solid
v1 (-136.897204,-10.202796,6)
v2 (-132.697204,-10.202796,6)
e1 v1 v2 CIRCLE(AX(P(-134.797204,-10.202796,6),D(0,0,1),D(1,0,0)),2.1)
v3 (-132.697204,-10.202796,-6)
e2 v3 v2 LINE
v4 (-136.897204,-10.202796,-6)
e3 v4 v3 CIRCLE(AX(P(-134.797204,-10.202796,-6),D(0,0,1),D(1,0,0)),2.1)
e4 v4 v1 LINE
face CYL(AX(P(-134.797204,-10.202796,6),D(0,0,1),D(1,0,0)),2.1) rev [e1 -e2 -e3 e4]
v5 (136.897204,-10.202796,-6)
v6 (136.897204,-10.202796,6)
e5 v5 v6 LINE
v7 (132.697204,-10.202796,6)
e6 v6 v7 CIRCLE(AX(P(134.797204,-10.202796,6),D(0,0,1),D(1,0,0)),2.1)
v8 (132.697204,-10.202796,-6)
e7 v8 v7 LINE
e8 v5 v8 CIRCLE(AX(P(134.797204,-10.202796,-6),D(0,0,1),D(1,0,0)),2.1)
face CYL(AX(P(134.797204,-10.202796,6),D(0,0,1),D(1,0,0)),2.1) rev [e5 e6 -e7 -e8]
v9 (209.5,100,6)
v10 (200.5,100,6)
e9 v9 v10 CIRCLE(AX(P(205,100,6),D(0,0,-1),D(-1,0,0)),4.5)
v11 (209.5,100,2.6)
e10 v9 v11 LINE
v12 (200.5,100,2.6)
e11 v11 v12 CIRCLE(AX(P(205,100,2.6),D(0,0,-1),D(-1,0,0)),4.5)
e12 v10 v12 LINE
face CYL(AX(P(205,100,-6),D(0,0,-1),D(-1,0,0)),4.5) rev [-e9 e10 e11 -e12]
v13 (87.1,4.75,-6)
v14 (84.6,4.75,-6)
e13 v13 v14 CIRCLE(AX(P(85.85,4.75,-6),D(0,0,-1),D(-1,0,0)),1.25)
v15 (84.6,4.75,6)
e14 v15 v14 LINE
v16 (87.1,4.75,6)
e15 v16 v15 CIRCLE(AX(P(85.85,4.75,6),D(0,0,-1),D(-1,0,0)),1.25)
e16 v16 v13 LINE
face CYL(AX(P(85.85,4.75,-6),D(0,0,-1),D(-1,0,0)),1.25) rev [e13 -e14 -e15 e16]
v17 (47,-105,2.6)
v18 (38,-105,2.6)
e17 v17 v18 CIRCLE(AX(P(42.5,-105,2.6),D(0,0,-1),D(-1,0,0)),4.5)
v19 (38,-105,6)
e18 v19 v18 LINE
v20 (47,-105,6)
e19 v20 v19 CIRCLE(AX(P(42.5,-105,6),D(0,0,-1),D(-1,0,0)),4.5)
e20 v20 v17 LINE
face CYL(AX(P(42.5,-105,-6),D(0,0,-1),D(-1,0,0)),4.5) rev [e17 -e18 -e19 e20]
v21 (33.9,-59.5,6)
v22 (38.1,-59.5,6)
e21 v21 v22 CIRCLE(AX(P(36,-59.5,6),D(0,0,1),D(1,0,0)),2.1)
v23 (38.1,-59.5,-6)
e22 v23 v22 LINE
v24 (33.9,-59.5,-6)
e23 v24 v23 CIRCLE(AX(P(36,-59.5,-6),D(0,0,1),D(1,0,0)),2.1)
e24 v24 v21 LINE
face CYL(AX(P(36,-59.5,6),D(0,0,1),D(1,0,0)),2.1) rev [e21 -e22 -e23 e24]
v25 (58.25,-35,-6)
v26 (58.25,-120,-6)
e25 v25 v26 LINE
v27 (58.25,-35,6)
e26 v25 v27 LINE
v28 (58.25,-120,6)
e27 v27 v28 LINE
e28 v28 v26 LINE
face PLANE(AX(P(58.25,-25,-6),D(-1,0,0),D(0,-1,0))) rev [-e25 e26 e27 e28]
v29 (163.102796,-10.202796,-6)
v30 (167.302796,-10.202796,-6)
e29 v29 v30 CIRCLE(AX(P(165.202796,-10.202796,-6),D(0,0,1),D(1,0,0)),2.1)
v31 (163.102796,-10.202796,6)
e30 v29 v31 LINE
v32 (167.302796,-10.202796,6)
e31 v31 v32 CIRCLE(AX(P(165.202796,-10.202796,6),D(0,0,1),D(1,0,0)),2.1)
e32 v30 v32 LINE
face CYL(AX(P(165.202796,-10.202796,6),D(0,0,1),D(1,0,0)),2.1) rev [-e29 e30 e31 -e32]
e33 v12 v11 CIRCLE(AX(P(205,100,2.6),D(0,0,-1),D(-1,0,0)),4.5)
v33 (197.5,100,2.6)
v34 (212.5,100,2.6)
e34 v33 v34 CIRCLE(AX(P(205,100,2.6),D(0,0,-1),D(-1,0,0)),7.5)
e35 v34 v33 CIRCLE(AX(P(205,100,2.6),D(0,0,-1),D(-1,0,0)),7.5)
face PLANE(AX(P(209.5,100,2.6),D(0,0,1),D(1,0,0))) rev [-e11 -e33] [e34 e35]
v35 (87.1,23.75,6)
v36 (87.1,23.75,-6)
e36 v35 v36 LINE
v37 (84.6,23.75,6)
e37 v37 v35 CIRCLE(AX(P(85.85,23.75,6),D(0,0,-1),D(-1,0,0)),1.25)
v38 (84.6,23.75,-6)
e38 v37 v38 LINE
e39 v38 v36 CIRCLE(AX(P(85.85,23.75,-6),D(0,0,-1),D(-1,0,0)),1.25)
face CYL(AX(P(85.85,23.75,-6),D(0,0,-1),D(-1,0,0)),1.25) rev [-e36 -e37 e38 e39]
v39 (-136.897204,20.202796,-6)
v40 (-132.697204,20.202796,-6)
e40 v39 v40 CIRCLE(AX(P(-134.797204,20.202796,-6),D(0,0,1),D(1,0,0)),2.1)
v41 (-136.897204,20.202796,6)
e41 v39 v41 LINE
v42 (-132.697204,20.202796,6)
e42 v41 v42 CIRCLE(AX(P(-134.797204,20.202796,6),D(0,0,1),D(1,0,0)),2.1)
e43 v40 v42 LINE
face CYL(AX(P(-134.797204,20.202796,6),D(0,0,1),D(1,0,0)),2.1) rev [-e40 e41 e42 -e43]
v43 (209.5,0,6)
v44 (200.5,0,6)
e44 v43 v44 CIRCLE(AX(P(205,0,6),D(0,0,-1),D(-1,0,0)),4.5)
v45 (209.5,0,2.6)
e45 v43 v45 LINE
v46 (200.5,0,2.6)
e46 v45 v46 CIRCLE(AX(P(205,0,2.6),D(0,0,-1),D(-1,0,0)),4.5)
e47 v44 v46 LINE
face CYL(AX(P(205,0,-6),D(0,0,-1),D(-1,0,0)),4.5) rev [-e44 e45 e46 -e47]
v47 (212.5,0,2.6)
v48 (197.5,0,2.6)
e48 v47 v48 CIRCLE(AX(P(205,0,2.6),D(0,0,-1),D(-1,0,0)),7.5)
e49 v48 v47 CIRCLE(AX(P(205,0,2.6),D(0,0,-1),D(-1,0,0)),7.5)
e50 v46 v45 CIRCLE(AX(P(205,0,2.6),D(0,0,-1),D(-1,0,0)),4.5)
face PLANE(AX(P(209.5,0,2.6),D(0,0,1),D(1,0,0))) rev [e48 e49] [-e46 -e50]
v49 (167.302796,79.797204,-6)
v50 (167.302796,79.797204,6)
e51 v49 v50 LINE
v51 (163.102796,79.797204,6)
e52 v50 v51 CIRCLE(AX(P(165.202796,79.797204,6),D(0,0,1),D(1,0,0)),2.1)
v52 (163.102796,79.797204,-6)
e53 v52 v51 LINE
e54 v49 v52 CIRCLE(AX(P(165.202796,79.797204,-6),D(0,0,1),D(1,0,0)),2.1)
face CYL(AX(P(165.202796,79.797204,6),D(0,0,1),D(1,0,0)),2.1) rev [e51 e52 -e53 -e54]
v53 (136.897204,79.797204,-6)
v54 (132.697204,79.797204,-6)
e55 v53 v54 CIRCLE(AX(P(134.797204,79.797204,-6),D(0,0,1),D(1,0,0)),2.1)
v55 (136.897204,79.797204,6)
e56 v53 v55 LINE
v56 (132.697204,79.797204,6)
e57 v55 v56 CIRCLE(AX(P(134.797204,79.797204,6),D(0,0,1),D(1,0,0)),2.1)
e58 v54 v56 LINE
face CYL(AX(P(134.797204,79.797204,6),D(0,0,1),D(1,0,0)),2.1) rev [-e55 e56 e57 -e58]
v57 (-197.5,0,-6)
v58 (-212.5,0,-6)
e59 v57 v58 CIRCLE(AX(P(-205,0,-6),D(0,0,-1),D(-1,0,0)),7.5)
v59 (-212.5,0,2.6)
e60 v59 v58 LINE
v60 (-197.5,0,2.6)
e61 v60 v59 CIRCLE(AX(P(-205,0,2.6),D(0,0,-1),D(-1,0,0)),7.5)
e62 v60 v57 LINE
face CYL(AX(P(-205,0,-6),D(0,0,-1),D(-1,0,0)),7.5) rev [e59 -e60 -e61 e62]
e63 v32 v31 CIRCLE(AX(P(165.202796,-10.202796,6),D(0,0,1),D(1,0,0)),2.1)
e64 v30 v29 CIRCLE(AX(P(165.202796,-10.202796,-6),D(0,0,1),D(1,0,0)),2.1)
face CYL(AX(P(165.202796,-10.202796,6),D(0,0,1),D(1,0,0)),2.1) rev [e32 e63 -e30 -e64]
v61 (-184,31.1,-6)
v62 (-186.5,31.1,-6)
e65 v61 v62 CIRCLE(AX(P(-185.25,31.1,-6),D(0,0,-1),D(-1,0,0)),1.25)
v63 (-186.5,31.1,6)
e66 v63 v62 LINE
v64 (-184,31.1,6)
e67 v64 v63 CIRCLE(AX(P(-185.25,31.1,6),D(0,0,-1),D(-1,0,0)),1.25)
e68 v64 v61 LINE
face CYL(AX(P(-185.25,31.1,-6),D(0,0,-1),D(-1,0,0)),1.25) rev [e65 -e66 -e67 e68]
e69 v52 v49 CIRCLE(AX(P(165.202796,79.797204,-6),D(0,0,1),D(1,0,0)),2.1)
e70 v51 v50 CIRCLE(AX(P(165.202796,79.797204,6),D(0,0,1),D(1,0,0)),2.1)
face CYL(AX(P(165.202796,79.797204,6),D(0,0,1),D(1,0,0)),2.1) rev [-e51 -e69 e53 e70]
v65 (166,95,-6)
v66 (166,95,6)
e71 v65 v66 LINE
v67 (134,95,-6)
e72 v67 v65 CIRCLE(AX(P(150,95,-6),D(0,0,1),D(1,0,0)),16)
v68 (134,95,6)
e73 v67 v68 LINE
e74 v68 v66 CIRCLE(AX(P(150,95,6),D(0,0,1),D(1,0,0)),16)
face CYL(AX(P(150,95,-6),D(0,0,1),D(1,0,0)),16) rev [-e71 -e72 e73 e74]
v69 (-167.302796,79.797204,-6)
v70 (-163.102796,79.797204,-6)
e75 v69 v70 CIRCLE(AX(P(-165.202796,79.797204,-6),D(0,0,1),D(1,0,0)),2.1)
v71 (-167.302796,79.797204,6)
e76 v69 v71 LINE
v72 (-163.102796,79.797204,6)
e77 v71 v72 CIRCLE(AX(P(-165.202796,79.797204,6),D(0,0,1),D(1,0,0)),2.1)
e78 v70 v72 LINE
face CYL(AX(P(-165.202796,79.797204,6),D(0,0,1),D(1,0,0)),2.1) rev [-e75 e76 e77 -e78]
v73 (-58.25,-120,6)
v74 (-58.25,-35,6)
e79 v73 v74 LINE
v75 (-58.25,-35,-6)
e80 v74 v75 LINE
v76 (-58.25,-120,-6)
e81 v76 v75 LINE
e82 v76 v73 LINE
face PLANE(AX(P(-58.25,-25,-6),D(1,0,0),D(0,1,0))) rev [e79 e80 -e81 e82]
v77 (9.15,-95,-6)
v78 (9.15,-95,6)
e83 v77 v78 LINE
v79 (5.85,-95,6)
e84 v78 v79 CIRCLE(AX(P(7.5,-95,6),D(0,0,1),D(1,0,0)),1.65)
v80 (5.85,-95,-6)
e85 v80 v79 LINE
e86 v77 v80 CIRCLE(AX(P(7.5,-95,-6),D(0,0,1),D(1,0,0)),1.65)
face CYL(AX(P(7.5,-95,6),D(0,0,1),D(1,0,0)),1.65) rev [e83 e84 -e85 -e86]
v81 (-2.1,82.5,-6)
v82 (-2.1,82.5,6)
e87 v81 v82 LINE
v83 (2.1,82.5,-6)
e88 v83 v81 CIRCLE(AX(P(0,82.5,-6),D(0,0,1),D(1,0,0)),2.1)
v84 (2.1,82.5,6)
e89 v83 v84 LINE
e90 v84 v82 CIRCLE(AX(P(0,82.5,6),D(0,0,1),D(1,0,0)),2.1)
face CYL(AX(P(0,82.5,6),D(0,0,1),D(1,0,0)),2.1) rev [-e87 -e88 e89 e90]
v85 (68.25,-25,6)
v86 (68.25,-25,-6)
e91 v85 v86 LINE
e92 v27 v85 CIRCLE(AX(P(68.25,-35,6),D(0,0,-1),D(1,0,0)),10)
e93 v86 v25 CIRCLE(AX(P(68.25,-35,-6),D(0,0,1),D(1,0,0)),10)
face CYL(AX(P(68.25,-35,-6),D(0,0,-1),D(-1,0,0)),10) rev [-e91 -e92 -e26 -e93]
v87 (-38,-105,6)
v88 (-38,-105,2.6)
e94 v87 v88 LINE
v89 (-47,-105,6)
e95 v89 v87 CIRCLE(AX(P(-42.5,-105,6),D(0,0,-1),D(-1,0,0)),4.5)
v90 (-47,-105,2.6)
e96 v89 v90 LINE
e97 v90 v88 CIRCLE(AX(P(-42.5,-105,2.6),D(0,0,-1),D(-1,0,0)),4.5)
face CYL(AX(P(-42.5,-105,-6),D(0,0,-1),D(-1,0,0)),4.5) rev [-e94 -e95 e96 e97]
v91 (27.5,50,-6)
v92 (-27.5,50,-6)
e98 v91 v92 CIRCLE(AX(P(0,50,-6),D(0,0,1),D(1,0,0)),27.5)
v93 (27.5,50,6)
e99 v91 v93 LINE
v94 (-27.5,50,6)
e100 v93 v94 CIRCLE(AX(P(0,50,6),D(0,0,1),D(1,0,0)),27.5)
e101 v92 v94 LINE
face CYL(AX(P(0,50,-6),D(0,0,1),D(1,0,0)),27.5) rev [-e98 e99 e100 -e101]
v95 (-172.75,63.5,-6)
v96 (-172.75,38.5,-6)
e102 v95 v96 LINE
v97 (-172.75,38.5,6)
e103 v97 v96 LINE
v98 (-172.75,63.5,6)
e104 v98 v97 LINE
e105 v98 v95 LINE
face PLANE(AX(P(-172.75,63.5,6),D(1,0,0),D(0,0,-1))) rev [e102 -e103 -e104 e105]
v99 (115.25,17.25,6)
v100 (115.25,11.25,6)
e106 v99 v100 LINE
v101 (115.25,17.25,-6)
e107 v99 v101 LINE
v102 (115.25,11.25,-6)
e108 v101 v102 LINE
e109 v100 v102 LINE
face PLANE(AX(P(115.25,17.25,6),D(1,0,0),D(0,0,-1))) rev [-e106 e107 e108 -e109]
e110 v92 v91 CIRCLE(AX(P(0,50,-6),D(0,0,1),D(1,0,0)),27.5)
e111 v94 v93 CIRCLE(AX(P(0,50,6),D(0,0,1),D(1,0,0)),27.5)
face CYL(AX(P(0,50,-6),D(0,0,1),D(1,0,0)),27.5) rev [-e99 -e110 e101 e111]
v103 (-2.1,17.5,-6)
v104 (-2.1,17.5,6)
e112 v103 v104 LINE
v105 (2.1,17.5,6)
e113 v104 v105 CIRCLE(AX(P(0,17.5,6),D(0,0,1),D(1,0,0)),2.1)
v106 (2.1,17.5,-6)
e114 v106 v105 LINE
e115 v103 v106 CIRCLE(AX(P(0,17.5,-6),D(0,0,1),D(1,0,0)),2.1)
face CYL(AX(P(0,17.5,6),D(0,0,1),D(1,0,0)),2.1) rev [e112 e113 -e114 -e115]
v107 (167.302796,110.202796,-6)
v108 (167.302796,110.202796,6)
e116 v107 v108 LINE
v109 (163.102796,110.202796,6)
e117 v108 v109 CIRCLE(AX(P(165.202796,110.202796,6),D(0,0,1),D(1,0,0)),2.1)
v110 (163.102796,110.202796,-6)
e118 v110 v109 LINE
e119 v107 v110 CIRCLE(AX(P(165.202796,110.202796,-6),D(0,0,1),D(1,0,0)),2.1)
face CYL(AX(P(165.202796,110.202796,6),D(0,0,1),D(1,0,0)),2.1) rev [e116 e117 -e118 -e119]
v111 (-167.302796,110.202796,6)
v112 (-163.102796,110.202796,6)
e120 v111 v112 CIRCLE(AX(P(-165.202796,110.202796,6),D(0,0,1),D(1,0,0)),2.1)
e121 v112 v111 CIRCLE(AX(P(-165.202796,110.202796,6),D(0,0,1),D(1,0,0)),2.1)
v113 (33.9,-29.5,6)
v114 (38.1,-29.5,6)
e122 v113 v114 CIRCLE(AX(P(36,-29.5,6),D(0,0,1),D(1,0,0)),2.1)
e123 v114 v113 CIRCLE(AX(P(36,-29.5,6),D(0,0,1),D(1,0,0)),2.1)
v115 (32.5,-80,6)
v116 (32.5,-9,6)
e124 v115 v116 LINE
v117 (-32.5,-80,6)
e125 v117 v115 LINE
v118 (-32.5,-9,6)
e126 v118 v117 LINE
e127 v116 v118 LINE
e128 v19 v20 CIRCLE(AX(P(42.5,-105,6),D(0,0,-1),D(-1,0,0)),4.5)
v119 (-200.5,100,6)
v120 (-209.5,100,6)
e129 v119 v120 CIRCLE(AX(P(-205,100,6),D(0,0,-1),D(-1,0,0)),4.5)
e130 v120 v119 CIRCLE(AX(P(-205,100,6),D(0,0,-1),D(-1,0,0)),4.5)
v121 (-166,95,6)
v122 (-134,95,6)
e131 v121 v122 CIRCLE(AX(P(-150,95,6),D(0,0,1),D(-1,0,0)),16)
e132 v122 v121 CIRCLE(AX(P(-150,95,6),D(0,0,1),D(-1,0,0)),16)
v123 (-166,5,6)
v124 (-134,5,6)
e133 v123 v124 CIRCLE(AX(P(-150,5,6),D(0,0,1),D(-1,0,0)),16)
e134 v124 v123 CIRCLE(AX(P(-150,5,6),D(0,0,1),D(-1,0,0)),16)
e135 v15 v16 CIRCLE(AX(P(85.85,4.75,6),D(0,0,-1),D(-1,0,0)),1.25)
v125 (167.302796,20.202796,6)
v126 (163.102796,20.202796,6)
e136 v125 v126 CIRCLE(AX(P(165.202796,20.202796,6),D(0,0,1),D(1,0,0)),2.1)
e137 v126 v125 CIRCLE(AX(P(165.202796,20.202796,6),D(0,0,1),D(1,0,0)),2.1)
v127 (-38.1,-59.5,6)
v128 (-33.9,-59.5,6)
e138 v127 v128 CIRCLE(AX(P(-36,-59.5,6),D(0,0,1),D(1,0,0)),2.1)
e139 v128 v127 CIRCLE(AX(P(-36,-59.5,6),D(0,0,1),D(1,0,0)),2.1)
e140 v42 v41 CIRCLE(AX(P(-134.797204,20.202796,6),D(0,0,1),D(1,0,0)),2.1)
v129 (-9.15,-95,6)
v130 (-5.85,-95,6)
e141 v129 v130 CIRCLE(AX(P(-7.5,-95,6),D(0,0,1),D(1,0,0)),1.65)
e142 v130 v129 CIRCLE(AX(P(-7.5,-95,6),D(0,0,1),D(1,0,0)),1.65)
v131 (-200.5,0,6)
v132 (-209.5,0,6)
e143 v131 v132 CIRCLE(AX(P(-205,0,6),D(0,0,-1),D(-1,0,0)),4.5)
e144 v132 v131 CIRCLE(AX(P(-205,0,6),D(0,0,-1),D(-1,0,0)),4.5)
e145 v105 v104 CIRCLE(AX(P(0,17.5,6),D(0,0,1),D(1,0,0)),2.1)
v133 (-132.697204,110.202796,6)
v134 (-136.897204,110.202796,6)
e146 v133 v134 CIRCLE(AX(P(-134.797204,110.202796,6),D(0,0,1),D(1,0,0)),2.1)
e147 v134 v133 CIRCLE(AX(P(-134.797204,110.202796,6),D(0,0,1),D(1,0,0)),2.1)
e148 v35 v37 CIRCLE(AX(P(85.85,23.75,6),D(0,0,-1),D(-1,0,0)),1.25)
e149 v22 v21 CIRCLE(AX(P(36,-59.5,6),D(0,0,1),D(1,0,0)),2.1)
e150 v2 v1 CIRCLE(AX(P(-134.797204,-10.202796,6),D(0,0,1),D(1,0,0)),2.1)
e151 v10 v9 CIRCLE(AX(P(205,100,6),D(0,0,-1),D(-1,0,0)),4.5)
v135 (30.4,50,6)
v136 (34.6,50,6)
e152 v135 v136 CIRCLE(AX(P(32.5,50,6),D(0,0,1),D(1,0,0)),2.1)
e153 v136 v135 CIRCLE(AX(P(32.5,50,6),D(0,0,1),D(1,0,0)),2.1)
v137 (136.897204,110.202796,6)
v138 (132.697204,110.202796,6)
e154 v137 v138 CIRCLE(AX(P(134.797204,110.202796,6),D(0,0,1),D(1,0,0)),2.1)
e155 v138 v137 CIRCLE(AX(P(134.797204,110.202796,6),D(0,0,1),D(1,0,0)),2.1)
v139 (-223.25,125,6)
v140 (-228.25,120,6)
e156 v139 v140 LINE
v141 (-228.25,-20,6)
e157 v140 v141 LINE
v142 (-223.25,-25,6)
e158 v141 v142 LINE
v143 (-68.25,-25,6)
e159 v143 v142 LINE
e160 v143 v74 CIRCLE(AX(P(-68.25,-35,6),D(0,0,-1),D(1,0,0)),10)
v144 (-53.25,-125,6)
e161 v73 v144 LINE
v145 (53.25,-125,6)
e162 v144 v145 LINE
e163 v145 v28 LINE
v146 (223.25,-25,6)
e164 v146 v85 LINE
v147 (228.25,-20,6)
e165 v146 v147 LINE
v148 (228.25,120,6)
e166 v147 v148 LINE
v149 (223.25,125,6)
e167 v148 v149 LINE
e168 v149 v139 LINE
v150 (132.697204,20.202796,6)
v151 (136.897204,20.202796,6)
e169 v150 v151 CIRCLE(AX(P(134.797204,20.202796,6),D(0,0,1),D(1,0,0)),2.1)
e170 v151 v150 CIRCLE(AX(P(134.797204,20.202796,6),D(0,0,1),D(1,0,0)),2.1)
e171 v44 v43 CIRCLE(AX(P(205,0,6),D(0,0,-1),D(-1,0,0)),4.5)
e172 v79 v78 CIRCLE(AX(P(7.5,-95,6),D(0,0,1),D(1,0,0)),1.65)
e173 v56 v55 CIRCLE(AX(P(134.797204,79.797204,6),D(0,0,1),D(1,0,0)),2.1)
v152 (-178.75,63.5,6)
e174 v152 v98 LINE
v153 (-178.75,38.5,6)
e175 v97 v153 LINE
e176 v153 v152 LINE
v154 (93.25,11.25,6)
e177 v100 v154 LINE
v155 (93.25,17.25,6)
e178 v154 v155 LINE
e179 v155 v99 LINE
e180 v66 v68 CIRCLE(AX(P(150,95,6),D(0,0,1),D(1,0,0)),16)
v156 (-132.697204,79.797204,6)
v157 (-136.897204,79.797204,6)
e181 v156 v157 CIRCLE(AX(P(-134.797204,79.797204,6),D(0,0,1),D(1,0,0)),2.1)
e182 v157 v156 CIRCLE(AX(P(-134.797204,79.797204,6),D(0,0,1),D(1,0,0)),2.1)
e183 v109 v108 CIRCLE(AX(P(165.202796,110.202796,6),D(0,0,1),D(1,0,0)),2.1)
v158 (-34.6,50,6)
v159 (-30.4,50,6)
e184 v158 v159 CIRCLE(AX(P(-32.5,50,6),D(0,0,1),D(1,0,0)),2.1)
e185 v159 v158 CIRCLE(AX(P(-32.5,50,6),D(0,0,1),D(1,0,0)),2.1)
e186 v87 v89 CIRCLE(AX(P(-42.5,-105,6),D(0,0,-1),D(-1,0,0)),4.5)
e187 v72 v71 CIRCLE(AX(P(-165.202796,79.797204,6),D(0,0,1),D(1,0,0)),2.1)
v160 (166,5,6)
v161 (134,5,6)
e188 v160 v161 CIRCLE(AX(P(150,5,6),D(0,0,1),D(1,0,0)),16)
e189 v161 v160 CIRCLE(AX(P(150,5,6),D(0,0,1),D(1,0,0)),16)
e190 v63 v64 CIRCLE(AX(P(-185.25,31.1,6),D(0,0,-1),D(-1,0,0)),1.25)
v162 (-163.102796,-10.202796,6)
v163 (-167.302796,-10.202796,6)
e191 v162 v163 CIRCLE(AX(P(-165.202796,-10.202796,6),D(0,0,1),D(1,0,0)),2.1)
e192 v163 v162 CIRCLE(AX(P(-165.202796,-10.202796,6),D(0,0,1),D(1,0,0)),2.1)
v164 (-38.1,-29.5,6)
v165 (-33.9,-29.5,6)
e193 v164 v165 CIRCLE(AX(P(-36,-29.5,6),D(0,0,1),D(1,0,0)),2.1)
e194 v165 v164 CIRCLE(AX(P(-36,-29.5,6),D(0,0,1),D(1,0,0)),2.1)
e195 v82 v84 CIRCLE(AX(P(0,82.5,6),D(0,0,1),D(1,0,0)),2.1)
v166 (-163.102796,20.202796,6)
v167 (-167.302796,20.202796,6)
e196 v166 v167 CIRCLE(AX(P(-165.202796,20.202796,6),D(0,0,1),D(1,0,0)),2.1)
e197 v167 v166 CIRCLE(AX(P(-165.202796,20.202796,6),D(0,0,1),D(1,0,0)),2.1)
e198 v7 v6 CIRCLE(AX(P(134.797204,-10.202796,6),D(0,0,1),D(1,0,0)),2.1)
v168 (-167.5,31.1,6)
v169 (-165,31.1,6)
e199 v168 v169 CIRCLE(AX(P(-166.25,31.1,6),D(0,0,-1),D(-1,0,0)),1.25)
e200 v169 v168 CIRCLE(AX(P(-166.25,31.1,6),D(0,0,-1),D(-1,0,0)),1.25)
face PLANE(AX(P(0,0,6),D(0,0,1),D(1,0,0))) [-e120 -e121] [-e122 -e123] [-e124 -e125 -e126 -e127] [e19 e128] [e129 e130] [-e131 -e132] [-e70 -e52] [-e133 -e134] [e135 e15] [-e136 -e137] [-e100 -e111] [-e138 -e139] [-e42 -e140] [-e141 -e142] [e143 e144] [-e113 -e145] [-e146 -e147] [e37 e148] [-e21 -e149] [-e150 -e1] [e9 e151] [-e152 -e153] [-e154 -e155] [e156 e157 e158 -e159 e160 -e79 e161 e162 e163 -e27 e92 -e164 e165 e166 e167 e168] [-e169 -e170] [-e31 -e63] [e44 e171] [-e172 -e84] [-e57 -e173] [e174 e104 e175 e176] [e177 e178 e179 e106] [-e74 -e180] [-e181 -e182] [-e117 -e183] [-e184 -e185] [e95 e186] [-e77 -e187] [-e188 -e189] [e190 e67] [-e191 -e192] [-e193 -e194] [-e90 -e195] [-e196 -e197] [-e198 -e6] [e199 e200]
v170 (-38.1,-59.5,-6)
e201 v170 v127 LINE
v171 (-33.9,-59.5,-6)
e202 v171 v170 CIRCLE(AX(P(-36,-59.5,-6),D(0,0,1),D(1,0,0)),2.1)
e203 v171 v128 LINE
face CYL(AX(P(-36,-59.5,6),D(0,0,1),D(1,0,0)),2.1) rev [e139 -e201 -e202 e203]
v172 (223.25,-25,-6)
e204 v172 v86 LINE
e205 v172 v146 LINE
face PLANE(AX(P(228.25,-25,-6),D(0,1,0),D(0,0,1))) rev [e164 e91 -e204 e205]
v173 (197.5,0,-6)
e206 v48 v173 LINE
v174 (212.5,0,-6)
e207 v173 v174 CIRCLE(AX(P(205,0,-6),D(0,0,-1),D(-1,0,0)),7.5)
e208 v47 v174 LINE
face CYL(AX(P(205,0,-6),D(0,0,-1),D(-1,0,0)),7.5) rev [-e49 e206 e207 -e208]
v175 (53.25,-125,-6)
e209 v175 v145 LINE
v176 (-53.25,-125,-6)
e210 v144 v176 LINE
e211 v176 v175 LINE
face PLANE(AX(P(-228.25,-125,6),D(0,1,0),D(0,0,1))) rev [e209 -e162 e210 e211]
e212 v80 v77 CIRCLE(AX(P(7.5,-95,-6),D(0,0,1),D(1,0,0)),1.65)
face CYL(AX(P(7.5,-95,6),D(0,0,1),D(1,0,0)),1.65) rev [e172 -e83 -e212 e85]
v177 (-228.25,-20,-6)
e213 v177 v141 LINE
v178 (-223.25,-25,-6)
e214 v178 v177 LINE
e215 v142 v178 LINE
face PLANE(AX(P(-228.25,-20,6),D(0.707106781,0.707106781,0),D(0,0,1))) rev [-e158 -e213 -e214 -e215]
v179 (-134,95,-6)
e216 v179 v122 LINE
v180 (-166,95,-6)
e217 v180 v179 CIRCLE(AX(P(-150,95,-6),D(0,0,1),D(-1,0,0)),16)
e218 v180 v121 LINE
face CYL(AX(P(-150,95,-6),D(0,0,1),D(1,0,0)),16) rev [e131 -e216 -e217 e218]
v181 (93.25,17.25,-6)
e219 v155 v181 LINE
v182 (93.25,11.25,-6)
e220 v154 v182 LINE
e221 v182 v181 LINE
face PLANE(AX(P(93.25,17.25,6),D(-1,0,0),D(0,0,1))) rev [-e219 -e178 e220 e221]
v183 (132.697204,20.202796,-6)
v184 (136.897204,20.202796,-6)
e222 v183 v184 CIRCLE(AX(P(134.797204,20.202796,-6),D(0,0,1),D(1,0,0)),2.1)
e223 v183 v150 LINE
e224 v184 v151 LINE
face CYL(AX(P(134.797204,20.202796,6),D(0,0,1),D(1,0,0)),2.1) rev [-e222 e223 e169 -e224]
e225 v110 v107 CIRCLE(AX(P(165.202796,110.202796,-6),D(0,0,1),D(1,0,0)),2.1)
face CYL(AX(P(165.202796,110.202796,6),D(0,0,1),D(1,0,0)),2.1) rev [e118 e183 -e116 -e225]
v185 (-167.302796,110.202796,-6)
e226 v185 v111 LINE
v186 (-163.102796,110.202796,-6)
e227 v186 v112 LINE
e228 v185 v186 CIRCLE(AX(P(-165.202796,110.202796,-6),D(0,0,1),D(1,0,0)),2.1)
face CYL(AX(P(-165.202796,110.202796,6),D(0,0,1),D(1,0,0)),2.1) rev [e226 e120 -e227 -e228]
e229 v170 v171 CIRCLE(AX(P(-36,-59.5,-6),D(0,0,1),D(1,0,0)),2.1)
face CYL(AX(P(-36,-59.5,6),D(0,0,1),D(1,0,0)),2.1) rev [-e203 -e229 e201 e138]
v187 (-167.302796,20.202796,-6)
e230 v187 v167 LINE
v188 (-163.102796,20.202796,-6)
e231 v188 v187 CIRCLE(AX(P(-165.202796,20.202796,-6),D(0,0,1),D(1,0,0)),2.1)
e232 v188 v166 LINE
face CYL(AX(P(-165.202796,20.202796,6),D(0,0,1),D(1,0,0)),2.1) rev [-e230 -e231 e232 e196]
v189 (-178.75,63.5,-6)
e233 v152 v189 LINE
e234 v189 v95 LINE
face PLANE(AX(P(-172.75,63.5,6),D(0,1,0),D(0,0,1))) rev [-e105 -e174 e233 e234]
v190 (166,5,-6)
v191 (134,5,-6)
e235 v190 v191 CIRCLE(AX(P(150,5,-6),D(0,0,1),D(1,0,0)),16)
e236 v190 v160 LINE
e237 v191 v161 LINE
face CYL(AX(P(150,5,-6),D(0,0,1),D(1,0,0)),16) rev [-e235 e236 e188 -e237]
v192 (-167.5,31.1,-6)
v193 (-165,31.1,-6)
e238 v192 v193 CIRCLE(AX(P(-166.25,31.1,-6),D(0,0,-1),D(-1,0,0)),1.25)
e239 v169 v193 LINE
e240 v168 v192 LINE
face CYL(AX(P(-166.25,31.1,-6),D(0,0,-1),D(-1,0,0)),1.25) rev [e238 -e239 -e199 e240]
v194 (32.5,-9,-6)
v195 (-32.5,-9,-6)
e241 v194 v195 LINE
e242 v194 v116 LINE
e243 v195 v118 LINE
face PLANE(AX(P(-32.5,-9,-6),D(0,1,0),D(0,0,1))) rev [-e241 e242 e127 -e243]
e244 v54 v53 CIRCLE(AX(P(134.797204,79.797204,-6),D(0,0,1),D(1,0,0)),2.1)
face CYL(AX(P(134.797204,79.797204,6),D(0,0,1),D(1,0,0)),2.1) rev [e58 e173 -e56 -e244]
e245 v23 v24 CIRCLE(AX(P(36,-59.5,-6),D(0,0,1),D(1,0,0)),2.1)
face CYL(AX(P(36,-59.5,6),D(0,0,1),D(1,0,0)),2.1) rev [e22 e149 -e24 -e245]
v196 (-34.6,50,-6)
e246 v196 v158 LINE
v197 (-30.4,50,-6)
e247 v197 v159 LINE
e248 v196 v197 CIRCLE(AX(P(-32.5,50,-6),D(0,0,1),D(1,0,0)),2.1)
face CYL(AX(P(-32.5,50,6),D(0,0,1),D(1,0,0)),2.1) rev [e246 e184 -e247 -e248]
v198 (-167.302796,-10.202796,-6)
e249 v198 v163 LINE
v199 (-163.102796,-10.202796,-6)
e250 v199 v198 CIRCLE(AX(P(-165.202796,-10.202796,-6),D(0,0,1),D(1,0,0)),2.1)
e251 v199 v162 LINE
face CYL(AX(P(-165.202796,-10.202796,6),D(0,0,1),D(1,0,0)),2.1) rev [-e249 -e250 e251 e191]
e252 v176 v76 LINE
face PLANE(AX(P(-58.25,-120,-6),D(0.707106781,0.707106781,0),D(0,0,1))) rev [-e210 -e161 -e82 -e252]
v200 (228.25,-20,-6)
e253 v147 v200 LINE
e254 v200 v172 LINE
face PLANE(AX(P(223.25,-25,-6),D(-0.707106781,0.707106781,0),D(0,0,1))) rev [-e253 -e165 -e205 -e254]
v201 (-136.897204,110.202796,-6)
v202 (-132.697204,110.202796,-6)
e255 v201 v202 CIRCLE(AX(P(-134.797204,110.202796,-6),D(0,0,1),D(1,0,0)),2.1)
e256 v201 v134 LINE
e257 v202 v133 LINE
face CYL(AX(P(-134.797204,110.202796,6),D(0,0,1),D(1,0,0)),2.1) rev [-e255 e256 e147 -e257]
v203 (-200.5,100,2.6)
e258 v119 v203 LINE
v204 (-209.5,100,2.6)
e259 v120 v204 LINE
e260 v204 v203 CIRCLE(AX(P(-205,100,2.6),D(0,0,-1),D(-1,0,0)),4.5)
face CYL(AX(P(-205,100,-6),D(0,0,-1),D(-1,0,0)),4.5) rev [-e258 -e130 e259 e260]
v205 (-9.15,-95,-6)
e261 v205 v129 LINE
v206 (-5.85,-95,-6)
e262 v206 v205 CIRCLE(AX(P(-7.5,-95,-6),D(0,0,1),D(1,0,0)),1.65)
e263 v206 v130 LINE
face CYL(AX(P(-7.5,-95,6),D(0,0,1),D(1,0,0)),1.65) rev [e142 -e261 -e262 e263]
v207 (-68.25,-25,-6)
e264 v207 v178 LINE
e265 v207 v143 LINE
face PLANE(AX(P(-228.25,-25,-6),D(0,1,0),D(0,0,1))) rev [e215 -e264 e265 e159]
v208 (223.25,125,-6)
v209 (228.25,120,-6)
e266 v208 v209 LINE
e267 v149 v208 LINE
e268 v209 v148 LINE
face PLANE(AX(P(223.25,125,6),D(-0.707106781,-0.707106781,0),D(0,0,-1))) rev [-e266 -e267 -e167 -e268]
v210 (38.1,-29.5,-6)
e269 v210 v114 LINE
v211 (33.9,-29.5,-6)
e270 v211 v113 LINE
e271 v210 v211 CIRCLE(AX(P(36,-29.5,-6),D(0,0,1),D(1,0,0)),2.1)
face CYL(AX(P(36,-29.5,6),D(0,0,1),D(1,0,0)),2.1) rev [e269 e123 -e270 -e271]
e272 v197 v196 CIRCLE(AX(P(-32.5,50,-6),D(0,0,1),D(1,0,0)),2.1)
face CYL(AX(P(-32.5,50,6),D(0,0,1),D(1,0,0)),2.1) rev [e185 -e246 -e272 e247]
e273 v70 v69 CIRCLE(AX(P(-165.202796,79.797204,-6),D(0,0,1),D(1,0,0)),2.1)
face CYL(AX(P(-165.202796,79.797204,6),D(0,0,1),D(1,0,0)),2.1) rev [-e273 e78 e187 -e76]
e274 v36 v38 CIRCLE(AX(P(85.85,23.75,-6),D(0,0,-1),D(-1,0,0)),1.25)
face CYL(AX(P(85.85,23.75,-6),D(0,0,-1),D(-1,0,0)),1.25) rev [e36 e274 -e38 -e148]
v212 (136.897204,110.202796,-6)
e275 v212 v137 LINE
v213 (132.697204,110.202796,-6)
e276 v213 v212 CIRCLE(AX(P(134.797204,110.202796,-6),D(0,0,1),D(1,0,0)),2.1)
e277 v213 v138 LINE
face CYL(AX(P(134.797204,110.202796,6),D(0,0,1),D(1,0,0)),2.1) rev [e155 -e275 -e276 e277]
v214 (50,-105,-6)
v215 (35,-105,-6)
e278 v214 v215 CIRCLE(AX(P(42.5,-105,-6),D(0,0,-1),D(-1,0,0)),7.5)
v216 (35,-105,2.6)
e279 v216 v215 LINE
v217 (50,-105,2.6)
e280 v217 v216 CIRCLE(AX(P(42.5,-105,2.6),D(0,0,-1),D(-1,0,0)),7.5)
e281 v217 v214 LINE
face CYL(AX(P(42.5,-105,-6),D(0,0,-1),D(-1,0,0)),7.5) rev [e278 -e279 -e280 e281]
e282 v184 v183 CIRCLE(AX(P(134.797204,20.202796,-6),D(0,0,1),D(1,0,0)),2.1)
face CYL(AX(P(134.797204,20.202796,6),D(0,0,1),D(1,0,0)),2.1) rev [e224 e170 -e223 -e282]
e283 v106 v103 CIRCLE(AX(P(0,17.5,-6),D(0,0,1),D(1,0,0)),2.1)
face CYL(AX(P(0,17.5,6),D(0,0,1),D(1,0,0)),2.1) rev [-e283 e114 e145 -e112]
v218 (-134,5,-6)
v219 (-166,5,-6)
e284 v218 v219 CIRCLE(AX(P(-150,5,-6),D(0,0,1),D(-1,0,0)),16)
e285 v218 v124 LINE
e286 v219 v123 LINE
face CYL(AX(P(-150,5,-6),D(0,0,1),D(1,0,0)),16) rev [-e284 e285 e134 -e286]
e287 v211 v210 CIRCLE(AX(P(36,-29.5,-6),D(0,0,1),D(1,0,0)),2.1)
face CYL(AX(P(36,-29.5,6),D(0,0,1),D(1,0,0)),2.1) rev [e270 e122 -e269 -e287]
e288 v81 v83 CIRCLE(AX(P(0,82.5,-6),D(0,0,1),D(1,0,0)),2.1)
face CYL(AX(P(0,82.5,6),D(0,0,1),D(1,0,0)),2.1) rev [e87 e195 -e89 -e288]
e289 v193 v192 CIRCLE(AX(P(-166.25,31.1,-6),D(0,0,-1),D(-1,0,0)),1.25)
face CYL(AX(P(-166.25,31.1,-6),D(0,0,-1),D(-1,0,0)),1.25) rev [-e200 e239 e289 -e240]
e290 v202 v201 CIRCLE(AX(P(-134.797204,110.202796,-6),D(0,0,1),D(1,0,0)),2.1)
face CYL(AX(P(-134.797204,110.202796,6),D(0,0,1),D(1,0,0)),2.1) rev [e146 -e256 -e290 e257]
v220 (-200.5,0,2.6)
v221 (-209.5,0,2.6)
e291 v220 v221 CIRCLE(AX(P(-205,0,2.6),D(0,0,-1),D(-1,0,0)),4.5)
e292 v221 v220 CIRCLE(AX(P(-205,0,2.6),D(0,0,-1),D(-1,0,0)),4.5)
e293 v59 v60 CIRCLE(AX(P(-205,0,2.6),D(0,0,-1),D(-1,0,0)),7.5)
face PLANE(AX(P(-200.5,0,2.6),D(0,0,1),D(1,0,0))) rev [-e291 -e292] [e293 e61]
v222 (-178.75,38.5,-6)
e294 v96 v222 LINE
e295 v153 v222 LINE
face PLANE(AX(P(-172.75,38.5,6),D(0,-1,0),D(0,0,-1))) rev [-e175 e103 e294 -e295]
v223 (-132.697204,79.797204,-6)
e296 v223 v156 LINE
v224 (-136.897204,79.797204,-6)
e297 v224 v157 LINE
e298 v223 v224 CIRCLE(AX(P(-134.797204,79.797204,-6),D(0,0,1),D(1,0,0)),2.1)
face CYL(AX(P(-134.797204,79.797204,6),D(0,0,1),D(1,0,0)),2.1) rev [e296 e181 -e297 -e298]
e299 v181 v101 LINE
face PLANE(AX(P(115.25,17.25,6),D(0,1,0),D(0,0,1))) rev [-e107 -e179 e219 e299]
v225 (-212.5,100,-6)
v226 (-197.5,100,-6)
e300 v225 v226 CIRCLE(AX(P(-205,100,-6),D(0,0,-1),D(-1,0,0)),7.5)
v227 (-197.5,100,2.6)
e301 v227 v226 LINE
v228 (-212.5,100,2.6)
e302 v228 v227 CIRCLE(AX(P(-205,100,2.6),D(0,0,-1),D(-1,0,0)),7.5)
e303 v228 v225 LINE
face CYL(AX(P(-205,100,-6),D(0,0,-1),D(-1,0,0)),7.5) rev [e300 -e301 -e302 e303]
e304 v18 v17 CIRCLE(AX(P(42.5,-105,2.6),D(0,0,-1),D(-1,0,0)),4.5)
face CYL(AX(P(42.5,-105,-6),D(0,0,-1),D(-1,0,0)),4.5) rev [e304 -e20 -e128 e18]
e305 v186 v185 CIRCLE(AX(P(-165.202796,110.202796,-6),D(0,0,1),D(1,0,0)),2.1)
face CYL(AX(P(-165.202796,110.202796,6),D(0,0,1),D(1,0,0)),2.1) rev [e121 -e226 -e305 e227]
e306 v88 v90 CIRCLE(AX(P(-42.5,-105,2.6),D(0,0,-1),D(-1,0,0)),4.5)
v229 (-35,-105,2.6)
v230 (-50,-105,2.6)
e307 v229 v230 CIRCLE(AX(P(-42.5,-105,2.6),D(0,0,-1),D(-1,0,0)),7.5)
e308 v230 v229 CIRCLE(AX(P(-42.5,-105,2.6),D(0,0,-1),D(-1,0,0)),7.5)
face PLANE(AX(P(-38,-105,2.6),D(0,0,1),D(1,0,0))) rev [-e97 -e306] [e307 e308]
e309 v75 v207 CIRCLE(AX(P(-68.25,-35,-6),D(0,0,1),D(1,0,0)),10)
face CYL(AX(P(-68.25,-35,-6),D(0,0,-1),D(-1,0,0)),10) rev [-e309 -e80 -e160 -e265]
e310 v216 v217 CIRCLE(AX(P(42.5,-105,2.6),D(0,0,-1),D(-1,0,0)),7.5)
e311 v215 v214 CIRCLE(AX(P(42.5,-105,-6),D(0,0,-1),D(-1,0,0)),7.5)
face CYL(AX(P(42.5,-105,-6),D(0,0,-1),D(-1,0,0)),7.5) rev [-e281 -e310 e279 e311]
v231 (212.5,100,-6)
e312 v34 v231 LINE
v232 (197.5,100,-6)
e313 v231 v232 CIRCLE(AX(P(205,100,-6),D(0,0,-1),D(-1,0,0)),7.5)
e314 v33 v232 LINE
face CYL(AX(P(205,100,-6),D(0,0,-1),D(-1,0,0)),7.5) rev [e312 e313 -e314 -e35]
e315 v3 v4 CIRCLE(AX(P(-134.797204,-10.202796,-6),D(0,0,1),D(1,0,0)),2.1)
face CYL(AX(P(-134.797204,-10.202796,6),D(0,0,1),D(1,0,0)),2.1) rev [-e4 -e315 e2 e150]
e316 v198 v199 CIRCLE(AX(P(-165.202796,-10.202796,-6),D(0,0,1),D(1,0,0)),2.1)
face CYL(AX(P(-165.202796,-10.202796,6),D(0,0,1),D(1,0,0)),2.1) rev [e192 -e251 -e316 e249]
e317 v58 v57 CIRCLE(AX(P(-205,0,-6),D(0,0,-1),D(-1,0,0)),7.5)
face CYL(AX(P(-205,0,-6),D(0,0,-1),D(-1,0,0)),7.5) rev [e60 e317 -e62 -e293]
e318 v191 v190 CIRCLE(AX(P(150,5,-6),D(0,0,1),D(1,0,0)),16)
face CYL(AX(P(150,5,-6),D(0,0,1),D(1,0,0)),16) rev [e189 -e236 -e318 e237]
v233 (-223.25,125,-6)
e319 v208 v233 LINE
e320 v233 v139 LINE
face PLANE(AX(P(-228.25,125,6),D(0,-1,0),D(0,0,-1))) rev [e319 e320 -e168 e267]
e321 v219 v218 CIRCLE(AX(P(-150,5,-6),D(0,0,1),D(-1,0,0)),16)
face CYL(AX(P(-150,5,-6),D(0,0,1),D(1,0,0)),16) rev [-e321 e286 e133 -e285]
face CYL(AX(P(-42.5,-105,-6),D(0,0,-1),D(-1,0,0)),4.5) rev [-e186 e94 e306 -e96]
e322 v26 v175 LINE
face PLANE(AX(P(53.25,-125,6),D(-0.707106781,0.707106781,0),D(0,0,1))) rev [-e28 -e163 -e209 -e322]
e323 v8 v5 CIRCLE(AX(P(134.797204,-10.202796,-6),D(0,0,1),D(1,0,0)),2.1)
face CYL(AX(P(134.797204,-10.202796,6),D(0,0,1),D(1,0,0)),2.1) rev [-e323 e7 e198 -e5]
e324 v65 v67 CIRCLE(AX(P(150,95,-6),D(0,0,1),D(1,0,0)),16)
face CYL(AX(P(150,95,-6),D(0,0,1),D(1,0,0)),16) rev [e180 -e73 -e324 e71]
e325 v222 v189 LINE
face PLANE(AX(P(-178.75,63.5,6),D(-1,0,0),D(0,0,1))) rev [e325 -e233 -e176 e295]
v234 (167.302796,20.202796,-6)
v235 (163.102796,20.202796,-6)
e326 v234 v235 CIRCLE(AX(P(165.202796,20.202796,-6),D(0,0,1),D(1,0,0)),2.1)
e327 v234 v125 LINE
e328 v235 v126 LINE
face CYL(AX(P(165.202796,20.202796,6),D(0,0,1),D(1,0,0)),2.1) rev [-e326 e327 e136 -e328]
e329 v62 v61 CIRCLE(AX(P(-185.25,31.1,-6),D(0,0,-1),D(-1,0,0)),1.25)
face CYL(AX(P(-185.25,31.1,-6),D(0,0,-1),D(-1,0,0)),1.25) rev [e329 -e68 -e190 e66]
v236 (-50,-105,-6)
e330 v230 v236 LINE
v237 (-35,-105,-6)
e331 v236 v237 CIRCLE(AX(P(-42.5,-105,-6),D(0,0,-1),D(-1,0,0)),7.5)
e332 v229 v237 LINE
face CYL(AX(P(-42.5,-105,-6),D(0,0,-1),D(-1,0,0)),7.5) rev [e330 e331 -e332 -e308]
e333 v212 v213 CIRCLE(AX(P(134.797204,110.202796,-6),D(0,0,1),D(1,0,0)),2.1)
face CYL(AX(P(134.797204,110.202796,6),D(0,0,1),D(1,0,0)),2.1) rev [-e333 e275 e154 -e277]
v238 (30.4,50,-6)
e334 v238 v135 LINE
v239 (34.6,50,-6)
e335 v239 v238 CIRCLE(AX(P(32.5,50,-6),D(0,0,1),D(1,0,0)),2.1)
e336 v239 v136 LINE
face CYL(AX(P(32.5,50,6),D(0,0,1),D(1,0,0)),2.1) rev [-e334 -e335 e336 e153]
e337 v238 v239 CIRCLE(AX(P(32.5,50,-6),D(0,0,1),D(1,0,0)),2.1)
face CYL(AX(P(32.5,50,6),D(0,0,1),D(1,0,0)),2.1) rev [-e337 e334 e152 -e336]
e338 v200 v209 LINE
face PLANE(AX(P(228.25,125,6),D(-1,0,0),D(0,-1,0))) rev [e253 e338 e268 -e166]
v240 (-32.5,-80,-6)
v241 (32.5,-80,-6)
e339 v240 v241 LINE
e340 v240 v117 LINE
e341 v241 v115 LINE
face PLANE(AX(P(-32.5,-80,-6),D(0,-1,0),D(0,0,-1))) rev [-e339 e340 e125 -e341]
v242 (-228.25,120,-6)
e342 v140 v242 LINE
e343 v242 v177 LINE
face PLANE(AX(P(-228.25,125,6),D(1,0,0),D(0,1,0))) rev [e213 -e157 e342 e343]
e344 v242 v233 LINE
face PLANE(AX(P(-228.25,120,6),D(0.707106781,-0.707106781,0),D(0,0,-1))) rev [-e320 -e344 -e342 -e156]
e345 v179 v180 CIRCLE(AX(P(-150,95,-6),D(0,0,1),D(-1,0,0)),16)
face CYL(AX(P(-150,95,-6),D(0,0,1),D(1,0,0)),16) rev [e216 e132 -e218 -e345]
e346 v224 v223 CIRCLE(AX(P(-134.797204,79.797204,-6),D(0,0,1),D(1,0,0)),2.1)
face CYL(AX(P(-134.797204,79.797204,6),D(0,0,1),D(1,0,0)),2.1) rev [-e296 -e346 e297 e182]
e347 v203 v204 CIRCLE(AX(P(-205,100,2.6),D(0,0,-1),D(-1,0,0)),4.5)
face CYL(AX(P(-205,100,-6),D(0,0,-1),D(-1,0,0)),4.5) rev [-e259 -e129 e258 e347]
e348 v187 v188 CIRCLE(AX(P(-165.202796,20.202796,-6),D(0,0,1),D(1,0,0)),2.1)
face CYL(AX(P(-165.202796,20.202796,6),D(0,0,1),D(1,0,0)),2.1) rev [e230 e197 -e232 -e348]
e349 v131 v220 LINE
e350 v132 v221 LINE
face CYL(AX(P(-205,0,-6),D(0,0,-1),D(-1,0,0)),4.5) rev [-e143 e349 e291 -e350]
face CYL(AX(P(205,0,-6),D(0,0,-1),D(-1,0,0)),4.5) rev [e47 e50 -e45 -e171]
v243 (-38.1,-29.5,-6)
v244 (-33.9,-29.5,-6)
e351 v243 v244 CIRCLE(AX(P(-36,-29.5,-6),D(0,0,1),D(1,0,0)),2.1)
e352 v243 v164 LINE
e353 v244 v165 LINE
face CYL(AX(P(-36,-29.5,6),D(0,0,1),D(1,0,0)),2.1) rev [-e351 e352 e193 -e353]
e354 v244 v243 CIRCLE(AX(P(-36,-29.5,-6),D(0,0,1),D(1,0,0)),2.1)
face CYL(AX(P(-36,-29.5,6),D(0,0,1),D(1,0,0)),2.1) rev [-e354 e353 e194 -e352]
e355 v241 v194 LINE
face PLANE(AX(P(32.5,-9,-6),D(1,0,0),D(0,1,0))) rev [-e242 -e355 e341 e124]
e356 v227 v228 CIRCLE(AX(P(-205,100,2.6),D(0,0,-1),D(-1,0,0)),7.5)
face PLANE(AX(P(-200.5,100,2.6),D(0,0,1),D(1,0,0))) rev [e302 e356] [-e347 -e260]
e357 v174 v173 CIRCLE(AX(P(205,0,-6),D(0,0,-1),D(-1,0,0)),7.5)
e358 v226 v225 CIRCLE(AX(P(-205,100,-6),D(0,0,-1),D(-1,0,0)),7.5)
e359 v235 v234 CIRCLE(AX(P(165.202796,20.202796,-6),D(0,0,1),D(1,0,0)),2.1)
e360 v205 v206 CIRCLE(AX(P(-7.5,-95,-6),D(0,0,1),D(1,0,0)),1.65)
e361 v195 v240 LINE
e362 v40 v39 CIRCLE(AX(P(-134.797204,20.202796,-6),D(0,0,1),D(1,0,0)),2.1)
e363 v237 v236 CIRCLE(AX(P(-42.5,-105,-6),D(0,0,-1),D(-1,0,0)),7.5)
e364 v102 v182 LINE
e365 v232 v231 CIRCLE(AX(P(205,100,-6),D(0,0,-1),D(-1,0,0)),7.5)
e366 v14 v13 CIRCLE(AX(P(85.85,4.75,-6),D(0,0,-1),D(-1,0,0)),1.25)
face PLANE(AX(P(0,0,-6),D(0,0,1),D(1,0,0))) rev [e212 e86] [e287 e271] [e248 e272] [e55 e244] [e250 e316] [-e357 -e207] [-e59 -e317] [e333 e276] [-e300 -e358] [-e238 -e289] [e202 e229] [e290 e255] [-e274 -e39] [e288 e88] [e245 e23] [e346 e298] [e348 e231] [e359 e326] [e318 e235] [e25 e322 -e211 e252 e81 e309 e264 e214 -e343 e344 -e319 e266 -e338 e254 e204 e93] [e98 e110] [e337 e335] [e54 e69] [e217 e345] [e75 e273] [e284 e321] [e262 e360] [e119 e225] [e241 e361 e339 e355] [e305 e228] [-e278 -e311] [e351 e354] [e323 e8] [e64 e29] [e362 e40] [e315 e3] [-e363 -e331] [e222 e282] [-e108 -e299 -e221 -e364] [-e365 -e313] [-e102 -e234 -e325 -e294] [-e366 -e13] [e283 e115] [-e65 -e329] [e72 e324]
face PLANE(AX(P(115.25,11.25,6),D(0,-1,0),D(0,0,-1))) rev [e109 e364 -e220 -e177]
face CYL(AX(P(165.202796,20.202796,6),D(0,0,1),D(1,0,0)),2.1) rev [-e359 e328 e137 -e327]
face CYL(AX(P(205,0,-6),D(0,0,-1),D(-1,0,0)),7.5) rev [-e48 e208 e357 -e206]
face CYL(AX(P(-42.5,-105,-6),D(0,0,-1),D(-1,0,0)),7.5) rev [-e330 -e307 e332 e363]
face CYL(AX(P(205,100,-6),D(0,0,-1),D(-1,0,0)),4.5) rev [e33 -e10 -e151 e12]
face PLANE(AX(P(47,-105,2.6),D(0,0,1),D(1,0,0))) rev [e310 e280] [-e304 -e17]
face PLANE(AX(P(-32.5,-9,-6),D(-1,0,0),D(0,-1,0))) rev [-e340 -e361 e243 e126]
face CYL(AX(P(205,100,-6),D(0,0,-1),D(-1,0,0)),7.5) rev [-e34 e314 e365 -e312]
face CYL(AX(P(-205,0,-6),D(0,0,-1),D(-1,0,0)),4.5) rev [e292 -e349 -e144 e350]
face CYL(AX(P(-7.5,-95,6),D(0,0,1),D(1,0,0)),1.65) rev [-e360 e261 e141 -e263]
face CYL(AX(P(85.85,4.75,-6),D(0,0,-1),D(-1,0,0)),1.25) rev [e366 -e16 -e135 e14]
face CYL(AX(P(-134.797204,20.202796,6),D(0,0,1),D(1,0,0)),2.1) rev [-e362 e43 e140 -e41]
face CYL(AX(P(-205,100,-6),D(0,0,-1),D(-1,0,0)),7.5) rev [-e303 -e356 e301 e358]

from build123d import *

# Parameters (mm, degrees)
SKETCH1_W                                           = 456.5
SKETCH1_H                                           = 250
BOSS_EXTRUDE1_DEPTH                                 = 6
SKETCH2_W                                           = 170
SKETCH2_H                                           = 100
CUT_EXTRUDE1_DEPTH                                  = 12
SKETCH3_R                                           = 16
CUT_EXTRUDE2_DEPTH                                  = 261.513075488
M5_TAPPED_HOLE1_D                                   = 4.2
SKETCH6_R                                           = 27.5
CUT_EXTRUDE3_DEPTH                                  = 261.513075488
M5_TAPPED_HOLE2_D                                   = 4.2
SKETCH9_W                                           = 65
SKETCH9_H                                           = 71
CUT_EXTRUDE4_DEPTH                                  = 261.513075488
M5_TAPPED_HOLE3_D                                   = 4.2
M4_TAPPED_HOLE1_D                                   = 3.3
SKETCH14_W                                          = 22
SKETCH14_H                                          = 6
SKETCH14_W_2                                        = 6
SKETCH14_H_2                                        = 25
CUT_EXTRUDE5_DEPTH                                  = 261.513075488
M3_TAPPED_HOLE1_D                                   = 2.5
FILLET1_R                                           = 10
CHAMFER1_SIZE                                       = 5
CBORE_FOR_M8_HEX_SOCKET_HEAD_CAP_SCREW1_D           = 9
CBORE_FOR_M8_HEX_SOCKET_HEAD_CAP_SCREW1_CBORE_D     = 15
CBORE_FOR_M8_HEX_SOCKET_HEAD_CAP_SCREW1_CBORE_DEPTH = 8.6


with BuildPart() as part:
    # Sketch1 → Boss-Extrude1 (new, symmetric)
    with BuildSketch(Plane.XY):
        Rectangle(SKETCH1_W, SKETCH1_H)
    extrude(amount=BOSS_EXTRUDE1_DEPTH, both=True)

    # Sketch2 → Cut-Extrude1 (cut)
    with BuildSketch(Plane.XY.offset(6)):
        with Locations((-143.25, -75)):
            Rectangle(SKETCH2_W, SKETCH2_H)
        with Locations((143.25, -75)):
            Rectangle(SKETCH2_W, SKETCH2_H)
    extrude(amount=-CUT_EXTRUDE1_DEPTH, mode=Mode.SUBTRACT)

    # Sketch3 → Cut-Extrude2 (cut, through all)
    with BuildSketch(Plane.XY.offset(6)):
        with Locations((150, 95)):
            Circle(SKETCH3_R)
        with Locations((150, 5)):
            Circle(SKETCH3_R)
        with Locations(Location((-150, 5, 0), (0, 0, 180))):
            Circle(SKETCH3_R)
        with Locations(Location((-150, 95, 0), (0, 0, 180))):
            Circle(SKETCH3_R)
    extrude(amount=-CUT_EXTRUDE2_DEPTH, mode=Mode.SUBTRACT)

    # M5 Tapped Hole1 (through all)
    with Locations(Plane.XY.offset(6)):
        with Locations((134.797204204, 110.202795796), (165.202795796, 110.202795796), (134.797204204, 79.797204204), (165.202795796, 79.797204204), (134.797204204, 20.202795796), (165.202795796, 20.202795796), (134.797204204, -10.202795796), (165.202795796, -10.202795796), (-134.797204204, -10.202795796), (-165.202795796, -10.202795796), (-134.797204204, 20.202795796), (-165.202795796, 20.202795796), (-134.797204204, 79.797204204), (-165.202795796, 79.797204204), (-134.797204204, 110.202795796), (-165.202795796, 110.202795796)):
            Hole(M5_TAPPED_HOLE1_D / 2)

    # Sketch6 → Cut-Extrude3 (cut, through all)
    with BuildSketch(Plane.XY.offset(6)):
        with Locations((0, 50)):
            Circle(SKETCH6_R)
    extrude(amount=-CUT_EXTRUDE3_DEPTH, mode=Mode.SUBTRACT)

    # M5 Tapped Hole2 (through all)
    with Locations(Plane.XY.offset(6)):
        with Locations((32.5, 50), (0, 82.5), (-32.5, 50), (0, 17.5)):
            Hole(M5_TAPPED_HOLE2_D / 2)

    # Sketch9 → Cut-Extrude4 (cut, through all)
    with BuildSketch(Plane.XY.offset(6)):
        with Locations((0, -44.5)):
            Rectangle(SKETCH9_W, SKETCH9_H)
    extrude(amount=-CUT_EXTRUDE4_DEPTH, mode=Mode.SUBTRACT)

    # M5 Tapped Hole3 (through all)
    with Locations(Plane.XY.offset(6)):
        with Locations((36, -29.5), (36, -59.5), (-36, -59.5), (-36, -29.5)):
            Hole(M5_TAPPED_HOLE3_D / 2)

    # M4 Tapped Hole1 (through all)
    with Locations(Plane.XY.offset(6)):
        with Locations((-7.5, -95), (7.5, -95)):
            Hole(M4_TAPPED_HOLE1_D / 2)

    # Sketch14 → Cut-Extrude5 (cut, through all)
    with BuildSketch(Plane(origin=(0, 0, -6), x_dir=(-1, 0, 0), z_dir=(0, 0, -1))):
        with Locations((-104.25, 14.25)):
            Rectangle(SKETCH14_W, SKETCH14_H)
        with Locations((175.75, 51)):
            Rectangle(SKETCH14_W_2, SKETCH14_H_2)
    extrude(amount=-CUT_EXTRUDE5_DEPTH, mode=Mode.SUBTRACT)

    # M3 Tapped Hole1 (through all)
    with Locations(Plane(origin=(0, 0, -6), x_dir=(-1, 0, 0), z_dir=(0, 0, -1))):
        with Locations((-85.85, 23.75), (185.25, 31.1), (-85.85, 4.75), (166.25, 31.1)):
            Hole(M3_TAPPED_HOLE1_D / 2)

    # Fillet1
    fillet1_edges = [part.edges().sort_by_distance(p)[0] for p in [
        (-58.25, -25, 0),
        (58.25, -25, 0),
    ]]
    fillet(fillet1_edges, radius=FILLET1_R)

    # Chamfer1
    chamfer1_edges = [part.edges().sort_by_distance(p)[0] for p in [
        (-228.25, -25, 0),
        (-58.25, -125, 0),
        (228.25, -25, 0),
        (58.25, -125, 0),
        (-228.25, 125, 0),
        (228.25, 125, 0),
    ]]
    chamfer(chamfer1_edges, length=CHAMFER1_SIZE)

    # CBORE for M8 Hex Socket Head Cap Screw1 (through all)
    with Locations(Plane(origin=(0, 0, -6), x_dir=(-1, 0, 0), z_dir=(0, 0, -1))):
        with Locations((-205, 100), (-205, 0), (205, 0), (205, 100), (-42.5, -105), (42.5, -105)):
            CounterBoreHole(CBORE_FOR_M8_HEX_SOCKET_HEAD_CAP_SCREW1_D / 2, CBORE_FOR_M8_HEX_SOCKET_HEAD_CAP_SCREW1_CBORE_D / 2, CBORE_FOR_M8_HEX_SOCKET_HEAD_CAP_SCREW1_CBORE_DEPTH)


solid = part.part
